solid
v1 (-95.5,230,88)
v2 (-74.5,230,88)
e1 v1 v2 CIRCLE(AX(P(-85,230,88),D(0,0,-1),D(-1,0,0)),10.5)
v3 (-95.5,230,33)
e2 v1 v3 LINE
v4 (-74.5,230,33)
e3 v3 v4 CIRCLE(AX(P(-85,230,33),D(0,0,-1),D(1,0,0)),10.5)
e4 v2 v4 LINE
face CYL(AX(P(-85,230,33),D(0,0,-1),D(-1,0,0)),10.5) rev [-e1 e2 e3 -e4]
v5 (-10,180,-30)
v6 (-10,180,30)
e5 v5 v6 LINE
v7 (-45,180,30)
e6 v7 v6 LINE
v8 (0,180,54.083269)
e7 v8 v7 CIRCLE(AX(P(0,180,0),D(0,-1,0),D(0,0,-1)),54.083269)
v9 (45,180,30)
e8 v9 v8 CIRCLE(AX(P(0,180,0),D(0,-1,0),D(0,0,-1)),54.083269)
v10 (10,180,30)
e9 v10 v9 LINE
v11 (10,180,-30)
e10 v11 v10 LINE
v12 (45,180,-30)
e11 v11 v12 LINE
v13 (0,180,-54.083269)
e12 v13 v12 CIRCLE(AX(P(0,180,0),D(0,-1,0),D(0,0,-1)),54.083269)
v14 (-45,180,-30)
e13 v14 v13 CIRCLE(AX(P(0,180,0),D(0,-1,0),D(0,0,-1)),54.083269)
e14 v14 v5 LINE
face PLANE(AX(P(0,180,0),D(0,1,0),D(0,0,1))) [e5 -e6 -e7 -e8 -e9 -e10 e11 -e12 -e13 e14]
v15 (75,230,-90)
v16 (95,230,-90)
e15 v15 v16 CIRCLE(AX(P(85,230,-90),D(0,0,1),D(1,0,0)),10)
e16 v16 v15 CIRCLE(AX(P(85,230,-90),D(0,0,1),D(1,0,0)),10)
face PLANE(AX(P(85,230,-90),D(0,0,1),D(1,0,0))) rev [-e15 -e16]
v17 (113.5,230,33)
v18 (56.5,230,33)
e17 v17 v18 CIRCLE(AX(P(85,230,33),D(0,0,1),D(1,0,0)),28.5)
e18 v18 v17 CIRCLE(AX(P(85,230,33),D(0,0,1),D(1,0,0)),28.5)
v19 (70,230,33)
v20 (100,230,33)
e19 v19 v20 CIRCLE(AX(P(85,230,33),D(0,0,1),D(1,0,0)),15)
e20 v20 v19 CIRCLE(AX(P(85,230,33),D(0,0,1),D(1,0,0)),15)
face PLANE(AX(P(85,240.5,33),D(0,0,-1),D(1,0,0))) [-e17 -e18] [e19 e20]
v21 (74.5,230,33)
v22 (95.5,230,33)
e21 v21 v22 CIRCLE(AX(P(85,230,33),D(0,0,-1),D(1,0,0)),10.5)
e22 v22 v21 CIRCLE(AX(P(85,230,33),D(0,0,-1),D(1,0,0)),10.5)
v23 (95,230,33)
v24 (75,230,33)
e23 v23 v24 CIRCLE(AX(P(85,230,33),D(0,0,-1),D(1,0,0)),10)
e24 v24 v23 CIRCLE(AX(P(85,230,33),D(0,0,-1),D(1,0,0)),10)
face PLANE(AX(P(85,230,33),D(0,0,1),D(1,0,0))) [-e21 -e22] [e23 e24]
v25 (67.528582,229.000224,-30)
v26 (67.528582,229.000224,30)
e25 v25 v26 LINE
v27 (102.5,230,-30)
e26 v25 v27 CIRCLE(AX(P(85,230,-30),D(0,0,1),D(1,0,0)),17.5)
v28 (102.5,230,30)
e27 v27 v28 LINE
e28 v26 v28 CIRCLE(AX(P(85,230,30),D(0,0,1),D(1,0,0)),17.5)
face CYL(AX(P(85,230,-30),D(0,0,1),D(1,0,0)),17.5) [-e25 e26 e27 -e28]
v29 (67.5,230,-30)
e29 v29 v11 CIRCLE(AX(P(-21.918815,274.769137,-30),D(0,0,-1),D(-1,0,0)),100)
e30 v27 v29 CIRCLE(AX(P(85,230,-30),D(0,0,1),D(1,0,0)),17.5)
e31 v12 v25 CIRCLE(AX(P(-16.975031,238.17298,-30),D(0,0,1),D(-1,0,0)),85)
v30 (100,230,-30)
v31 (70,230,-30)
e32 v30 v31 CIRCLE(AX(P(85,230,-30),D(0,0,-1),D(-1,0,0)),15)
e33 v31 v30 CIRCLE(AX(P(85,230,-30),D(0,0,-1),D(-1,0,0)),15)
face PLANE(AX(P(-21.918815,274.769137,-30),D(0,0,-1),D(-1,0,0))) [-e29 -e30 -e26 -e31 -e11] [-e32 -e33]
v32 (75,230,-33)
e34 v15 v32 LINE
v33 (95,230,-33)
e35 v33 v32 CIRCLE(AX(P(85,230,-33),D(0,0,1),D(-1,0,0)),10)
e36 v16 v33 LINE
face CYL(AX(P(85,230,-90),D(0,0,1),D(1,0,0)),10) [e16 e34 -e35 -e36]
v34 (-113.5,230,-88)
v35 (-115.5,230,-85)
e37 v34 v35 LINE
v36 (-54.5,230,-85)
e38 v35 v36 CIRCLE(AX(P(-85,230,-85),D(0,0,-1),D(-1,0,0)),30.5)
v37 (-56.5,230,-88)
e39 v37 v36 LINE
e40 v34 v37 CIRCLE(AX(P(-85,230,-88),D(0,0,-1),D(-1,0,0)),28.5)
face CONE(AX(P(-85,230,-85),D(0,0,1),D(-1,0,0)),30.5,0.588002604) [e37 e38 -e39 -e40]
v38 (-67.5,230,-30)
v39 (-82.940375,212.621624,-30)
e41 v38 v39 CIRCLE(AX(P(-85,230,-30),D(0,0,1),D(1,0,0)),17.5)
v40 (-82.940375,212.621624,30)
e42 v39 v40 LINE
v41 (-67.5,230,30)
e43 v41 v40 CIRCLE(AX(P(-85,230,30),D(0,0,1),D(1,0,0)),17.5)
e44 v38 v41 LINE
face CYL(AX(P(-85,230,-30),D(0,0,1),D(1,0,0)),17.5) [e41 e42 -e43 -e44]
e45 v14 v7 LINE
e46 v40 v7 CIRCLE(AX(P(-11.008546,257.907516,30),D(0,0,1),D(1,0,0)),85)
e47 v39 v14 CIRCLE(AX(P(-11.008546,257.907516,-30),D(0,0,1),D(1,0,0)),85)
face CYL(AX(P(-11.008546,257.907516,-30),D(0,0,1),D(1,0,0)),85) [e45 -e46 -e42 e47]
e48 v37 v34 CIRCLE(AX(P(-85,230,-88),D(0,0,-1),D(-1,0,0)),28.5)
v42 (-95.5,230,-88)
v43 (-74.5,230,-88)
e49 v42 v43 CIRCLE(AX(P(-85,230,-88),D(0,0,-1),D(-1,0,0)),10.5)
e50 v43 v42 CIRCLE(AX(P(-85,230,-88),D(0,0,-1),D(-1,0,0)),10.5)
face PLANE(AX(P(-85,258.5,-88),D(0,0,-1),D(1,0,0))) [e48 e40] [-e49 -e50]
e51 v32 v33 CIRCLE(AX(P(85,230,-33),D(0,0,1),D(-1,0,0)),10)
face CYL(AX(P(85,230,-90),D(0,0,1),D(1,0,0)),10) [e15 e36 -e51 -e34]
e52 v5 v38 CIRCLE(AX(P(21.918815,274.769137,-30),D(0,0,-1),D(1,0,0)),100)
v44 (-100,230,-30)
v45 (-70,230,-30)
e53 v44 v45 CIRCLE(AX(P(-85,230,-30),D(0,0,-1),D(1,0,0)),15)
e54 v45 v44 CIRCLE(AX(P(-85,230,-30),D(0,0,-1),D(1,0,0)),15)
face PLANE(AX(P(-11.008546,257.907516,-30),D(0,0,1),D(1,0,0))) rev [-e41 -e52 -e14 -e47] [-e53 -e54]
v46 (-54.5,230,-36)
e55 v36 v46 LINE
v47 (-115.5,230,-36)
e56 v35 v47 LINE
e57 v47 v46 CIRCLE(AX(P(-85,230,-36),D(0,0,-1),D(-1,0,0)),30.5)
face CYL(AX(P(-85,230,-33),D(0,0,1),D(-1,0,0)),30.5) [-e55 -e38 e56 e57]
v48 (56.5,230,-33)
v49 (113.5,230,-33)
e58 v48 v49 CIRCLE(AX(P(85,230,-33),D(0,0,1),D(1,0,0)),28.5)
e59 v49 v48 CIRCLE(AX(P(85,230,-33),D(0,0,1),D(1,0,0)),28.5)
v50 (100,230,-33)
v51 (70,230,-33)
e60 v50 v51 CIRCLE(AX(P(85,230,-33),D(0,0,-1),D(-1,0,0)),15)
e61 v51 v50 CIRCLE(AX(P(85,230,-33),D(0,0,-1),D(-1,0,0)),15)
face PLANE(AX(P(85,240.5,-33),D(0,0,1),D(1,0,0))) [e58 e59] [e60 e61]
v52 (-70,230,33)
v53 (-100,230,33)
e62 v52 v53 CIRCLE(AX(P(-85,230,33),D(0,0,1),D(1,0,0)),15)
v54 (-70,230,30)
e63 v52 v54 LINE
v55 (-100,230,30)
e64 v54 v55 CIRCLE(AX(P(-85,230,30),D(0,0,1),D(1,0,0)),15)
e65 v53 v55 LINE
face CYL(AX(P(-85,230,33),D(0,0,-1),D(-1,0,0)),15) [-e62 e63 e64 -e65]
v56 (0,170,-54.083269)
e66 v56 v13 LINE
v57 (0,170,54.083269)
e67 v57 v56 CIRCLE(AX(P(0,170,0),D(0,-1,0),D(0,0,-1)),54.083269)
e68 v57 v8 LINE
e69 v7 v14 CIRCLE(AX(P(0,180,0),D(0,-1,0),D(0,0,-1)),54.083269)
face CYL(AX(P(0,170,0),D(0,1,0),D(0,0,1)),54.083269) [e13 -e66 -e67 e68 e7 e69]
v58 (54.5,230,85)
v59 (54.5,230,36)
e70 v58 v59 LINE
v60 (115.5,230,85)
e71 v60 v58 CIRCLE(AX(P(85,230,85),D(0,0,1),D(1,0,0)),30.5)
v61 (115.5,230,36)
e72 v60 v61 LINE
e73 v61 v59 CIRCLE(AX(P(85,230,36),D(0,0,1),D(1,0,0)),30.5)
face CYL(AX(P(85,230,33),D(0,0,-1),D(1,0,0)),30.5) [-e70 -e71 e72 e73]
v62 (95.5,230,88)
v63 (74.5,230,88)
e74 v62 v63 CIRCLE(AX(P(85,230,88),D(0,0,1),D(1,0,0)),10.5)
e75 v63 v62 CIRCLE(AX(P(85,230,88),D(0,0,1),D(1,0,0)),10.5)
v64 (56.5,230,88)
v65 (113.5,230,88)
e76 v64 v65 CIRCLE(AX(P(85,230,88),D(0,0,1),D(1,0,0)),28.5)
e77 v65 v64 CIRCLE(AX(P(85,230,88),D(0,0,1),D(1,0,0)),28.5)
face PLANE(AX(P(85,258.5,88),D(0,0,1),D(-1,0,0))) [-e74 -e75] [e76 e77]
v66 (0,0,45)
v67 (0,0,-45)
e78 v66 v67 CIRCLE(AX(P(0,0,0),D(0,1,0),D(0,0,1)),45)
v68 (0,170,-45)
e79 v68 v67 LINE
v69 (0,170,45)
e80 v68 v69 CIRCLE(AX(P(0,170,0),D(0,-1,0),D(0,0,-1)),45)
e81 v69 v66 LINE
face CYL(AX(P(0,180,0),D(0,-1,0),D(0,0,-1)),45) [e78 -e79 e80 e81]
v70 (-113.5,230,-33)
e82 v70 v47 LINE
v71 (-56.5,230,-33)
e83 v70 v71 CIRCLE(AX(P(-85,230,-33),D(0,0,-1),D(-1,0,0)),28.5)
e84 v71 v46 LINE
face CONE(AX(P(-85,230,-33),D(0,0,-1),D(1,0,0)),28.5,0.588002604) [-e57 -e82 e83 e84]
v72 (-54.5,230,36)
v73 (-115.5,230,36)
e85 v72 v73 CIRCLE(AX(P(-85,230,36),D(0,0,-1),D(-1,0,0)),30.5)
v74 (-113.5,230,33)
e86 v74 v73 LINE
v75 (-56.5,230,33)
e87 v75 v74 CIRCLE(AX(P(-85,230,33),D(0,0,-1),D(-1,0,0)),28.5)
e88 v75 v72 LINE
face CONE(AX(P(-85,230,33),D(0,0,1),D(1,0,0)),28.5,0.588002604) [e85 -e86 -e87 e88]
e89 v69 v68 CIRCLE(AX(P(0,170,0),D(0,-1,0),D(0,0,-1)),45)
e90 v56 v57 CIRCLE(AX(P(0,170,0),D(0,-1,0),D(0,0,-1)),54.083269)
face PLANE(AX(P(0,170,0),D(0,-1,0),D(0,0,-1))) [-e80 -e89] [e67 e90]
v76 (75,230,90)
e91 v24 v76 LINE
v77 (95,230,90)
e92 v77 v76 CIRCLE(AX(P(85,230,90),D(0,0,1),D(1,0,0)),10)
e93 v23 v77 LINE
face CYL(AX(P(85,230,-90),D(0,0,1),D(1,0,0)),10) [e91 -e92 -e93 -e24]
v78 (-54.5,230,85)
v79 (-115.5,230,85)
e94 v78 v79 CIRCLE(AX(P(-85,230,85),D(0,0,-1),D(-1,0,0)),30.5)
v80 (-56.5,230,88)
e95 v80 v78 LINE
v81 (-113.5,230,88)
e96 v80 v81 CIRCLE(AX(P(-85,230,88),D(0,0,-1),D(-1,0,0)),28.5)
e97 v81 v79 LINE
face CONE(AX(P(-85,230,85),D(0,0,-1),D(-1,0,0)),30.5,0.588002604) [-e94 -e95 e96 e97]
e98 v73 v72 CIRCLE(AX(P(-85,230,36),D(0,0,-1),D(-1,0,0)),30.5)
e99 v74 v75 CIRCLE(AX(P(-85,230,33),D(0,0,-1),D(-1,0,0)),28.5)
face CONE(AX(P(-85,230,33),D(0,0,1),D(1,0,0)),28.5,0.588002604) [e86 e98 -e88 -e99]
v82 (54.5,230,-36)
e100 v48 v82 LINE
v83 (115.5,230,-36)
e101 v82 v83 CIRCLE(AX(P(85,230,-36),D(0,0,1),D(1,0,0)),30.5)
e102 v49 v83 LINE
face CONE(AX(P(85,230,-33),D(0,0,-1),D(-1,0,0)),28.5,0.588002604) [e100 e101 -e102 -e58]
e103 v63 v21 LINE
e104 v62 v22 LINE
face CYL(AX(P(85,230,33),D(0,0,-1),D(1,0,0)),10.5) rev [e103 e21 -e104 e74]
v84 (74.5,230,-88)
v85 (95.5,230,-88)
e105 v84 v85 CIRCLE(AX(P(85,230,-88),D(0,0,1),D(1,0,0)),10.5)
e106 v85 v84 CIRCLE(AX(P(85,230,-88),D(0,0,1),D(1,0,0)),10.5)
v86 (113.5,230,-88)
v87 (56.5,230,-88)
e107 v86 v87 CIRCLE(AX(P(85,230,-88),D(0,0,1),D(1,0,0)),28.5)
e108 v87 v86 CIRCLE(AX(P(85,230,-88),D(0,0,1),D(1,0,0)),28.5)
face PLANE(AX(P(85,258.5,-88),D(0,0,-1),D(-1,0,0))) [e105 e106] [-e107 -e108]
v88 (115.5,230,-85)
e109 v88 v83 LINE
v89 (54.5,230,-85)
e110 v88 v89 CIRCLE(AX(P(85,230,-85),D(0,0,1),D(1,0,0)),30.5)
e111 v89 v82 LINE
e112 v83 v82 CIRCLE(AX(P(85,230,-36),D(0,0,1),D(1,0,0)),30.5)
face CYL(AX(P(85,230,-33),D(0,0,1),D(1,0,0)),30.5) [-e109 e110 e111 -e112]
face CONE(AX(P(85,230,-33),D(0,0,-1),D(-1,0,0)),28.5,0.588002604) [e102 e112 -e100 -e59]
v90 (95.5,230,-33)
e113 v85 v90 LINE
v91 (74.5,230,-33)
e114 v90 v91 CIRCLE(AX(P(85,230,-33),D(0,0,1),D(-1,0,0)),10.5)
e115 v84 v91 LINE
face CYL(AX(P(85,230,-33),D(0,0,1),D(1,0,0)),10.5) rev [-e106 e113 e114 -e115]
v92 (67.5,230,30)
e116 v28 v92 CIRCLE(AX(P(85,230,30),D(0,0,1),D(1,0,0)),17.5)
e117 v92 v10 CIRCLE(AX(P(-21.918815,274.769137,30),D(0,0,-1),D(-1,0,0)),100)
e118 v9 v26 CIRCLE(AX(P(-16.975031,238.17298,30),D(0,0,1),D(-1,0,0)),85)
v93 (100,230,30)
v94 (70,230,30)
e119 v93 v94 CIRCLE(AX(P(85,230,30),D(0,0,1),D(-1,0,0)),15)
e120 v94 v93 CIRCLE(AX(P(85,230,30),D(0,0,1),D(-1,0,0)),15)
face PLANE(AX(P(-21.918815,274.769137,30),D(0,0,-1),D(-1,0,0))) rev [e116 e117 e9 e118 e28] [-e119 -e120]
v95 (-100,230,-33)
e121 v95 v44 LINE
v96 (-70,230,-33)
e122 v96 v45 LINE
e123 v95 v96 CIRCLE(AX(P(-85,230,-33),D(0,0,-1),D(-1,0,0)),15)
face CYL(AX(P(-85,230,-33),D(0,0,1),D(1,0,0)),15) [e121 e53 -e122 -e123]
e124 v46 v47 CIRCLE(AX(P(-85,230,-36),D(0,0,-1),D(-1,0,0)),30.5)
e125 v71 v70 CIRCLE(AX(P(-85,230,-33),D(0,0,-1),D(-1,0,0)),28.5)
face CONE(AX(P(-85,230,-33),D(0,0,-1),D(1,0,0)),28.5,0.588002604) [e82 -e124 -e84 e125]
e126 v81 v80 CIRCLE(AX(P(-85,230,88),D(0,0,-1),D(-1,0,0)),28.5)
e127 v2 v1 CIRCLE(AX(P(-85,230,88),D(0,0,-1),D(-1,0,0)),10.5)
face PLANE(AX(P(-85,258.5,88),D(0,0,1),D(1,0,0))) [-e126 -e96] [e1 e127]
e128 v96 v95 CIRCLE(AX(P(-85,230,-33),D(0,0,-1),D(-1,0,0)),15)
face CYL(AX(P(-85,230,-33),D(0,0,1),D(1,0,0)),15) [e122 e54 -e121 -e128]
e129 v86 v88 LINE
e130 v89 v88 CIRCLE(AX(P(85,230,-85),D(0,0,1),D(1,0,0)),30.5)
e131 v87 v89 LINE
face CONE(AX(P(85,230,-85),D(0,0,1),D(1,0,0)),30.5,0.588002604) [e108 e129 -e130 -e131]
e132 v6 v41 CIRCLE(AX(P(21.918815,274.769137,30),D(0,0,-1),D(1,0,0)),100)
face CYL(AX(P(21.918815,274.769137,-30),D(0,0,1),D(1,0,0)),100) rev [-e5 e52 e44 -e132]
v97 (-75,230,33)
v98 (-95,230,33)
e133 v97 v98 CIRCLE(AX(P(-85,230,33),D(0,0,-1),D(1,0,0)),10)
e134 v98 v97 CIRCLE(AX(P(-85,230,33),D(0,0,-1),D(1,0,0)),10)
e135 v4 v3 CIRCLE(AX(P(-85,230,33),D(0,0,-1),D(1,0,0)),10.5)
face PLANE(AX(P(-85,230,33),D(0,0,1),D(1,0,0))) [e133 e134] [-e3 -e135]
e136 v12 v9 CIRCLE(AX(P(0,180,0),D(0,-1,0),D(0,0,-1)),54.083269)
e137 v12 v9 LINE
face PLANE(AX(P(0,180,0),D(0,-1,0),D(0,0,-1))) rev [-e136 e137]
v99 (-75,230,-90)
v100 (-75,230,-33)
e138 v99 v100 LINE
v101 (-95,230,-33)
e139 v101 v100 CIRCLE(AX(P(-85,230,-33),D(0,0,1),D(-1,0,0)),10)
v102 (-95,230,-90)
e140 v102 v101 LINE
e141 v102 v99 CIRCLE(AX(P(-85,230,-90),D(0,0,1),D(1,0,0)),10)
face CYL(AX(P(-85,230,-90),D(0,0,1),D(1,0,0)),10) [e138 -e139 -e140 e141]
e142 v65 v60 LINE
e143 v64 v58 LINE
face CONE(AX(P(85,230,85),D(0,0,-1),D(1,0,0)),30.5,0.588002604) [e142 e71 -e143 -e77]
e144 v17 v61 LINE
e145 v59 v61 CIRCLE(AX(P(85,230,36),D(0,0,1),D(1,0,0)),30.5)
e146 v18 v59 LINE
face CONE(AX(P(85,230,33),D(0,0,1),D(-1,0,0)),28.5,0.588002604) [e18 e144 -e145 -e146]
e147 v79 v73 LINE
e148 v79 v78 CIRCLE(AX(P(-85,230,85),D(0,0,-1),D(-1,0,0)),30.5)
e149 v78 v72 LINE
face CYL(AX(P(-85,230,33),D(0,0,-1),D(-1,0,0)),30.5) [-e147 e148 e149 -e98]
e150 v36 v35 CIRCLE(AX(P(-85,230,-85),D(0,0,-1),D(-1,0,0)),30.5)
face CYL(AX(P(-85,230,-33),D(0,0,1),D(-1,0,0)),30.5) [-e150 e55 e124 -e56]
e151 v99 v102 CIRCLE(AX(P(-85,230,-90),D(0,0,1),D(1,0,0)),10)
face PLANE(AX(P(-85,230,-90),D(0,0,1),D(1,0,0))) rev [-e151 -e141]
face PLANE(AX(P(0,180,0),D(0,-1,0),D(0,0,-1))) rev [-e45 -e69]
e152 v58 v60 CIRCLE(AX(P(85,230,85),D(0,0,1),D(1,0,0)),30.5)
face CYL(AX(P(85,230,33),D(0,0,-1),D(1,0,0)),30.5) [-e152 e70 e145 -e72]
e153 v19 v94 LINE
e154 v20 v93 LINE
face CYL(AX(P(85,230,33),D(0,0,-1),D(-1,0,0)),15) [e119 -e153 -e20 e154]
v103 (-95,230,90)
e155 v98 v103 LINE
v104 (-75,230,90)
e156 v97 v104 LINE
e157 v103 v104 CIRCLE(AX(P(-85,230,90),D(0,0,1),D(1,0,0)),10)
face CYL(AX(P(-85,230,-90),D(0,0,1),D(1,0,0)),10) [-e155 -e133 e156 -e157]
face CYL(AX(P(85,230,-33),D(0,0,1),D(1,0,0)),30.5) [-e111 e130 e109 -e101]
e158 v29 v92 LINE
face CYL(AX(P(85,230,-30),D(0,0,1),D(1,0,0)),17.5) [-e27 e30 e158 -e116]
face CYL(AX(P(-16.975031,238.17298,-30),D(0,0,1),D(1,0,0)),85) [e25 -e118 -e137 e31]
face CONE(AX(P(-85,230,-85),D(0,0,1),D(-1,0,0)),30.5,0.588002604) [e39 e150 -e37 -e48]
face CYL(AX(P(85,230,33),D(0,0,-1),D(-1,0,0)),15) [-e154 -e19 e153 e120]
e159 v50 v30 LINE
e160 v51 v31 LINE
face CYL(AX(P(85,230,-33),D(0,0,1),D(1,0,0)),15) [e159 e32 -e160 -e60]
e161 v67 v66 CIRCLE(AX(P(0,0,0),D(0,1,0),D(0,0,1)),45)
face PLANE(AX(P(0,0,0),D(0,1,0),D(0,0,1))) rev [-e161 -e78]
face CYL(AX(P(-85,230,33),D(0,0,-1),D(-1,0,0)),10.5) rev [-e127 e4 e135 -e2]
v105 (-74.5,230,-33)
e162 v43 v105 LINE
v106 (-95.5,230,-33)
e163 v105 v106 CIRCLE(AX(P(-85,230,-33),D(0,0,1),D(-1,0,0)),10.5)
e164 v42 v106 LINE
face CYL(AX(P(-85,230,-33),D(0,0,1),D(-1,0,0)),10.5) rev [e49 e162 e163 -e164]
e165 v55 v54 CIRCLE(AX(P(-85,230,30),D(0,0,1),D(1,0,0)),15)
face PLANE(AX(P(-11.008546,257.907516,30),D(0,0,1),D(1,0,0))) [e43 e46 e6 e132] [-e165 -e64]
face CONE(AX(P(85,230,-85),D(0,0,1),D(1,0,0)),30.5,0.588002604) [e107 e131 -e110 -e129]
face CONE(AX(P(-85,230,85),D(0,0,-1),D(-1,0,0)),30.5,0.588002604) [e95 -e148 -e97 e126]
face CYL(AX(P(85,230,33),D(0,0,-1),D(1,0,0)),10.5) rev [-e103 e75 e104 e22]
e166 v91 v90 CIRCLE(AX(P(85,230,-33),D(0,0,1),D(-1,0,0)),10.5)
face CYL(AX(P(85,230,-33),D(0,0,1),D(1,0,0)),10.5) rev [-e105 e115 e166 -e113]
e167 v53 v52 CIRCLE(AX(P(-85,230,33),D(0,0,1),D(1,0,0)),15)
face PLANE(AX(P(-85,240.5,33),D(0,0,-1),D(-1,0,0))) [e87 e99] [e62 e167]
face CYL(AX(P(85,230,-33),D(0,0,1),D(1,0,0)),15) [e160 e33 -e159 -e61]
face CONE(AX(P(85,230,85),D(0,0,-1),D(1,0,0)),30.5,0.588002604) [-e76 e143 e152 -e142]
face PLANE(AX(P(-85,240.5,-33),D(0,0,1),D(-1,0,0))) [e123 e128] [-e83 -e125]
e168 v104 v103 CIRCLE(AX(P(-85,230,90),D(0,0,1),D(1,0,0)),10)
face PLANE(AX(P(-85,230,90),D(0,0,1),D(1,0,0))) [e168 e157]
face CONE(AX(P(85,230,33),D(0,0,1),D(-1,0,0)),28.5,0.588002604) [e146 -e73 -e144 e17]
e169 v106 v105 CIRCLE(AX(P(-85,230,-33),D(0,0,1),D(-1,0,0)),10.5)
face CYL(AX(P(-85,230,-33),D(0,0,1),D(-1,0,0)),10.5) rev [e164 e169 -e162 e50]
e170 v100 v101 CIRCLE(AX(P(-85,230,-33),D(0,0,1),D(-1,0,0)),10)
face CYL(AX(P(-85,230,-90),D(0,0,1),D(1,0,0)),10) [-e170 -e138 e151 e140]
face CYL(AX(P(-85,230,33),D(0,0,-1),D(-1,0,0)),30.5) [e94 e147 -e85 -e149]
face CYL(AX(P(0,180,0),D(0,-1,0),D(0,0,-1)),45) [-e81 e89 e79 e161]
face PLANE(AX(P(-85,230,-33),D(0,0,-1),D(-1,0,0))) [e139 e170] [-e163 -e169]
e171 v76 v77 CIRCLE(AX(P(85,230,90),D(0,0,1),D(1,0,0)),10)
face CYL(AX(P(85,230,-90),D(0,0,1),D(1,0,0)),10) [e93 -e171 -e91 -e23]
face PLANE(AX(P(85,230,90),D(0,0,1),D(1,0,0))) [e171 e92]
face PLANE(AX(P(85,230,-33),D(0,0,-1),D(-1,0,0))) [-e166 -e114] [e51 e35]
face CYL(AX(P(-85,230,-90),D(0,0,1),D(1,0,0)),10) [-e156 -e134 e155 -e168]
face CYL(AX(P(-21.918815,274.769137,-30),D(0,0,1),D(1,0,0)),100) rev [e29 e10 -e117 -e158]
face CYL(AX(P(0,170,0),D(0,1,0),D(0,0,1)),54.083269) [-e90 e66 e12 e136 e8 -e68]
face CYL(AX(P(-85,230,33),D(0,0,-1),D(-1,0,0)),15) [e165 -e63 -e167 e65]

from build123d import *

# Parameters (mm, degrees)
SKETCH1_R                  = 45
BOSS_EXTRUDE1_DEPTH        = 180
BOSS_EXTRUDE2_DEPTH        = 90
BOSS_EXTRUDE2_DEPTH_BACK   = 90
SKETCH3_R                  = 10
BOSS_EXTRUDE2_2_DEPTH      = 90
BOSS_EXTRUDE2_2_DEPTH_BACK = 90
BOSS_EXTRUDE3_DEPTH        = 30
BOSS_EXTRUDE3_DEPTH_BACK   = 30
SKETCH5_R                  = 54.083269132
BOSS_EXTRUDE4_DEPTH        = 10
SKETCH6_R                  = 15
BOSS_EXTRUDE5_DEPTH        = 3
BOSS_EXTRUDE6_START        = 3
SKETCH7_R                  = 15
BOSS_EXTRUDE6_DEPTH        = 3


with BuildPart() as part:
    # Sketch1 → Boss-Extrude1 (new body)
    with BuildSketch(Plane(origin=(0, 0, 0), x_dir=(1, 0, 0), z_dir=(0, 1, 0))):
        with Locations(Location((0, 0, 0), (0, 0, 90))):
            Circle(SKETCH1_R)
    extrude(amount=BOSS_EXTRUDE1_DEPTH)



with BuildPart() as body_2:
    # Sketch3 → Boss-Extrude2 (new, two sides: drawn at the far end of the back side and taken through both)
    with BuildSketch(Plane.XY.offset(-BOSS_EXTRUDE2_DEPTH_BACK)):
        with Locations((85, 230)):
            Circle(SKETCH3_R)
    extrude(amount=BOSS_EXTRUDE2_DEPTH + BOSS_EXTRUDE2_DEPTH_BACK)


with BuildPart() as body_3:
    # Sketch3 → Boss-Extrude2 2 (new, two sides: drawn at the far end of the back side and taken through both)
    with BuildSketch(Plane.XY.offset(-BOSS_EXTRUDE2_2_DEPTH_BACK)):
        with Locations((-85, 230)):
            Circle(SKETCH3_R)
    extrude(amount=BOSS_EXTRUDE2_2_DEPTH + BOSS_EXTRUDE2_2_DEPTH_BACK)


with BuildPart() as part_1:
    add(part.part)

    add(body_2.part)  # Boss-Extrude3 merges body 2

    add(body_3.part)  # Boss-Extrude3 merges body 3
    # Sketch4 → Boss-Extrude3 (add, two sides: drawn at the far end of the back side and taken through both)
    with BuildSketch(Plane.XY.offset(-BOSS_EXTRUDE3_DEPTH_BACK)):
        with BuildLine():
            Line((-45, 180), (-10, 180))
            ThreePointArc((-10, 180), (-43.69905694, 199.308584519), (-67.5, 230))
            ThreePointArc((-67.5, 230), (-98.082305532, 241.623393737), (-82.940375083, 212.621624207))
            ThreePointArc((-82.940375083, 212.621624207), (-66.424952125, 193.455813577), (-45, 180))
        make_face()
        with BuildLine():
            Line((10, 180), (45, 180))
            ThreePointArc((45, 180), (60.253550288, 202.66599047), (67.528581994, 229.00022359))
            ThreePointArc((67.528581994, 229.00022359), (102.492853042, 230.500092441), (67.5, 230))
            ThreePointArc((67.5, 230), (43.69905694, 199.308584519), (10, 180))
        make_face()
    extrude(amount=BOSS_EXTRUDE3_DEPTH + BOSS_EXTRUDE3_DEPTH_BACK)

    # Sketch5 → Boss-Extrude4 (add)
    with BuildSketch(Plane.XZ.offset(-180)):
        with Locations(Location((0, 0, 0), (0, 0, 33.690067526))):
            Circle(SKETCH5_R)
    extrude(amount=BOSS_EXTRUDE4_DEPTH)

    # Sketch6 → Boss-Extrude5 (add)
    with BuildSketch(Plane.XY.offset(30)):
        with Locations((-85, 230)):
            Circle(SKETCH6_R)
        with Locations(Location((85, 230, 0), (0, 0, 180))):
            Circle(SKETCH6_R)
    extrude(amount=BOSS_EXTRUDE5_DEPTH)

    # Sketch7 → Boss-Extrude6 (add)
    with BuildSketch(Plane(origin=(0, 0, -30), x_dir=(-1, 0, 0), z_dir=(0, 0, -1)).offset(BOSS_EXTRUDE6_START)):
        with Locations((-85, 230)):
            Circle(SKETCH7_R)
        with Locations(Location((85, 230, 0), (0, 0, 180))):
            Circle(SKETCH7_R)
    extrude(amount=-BOSS_EXTRUDE6_DEPTH)

    # Sketch8 → Revolve1 (revolve)
    with BuildSketch(Plane(origin=(-85, 0, 0), x_dir=(0, 0, -1), z_dir=(1, 0, 0)), mode=Mode.PRIVATE) as revolve1_sk:
        Polygon((-33, 240.5), (-33, 258.5), (-36, 260.5), (-85, 260.5), (-88, 258.5), (-88, 240.5), align=None)
    revolve1 = revolve(revolve1_sk.sketch.rotate(Axis((-85, 230, 33), (0, 0, 1)), 90), axis=Axis((-85, 230, 33), (0, 0, 1)))

    # Mirror1: Revolve1 across plane
    add(revolve1.mirror(Plane(origin=(0, 0, 0), x_dir=(0, 0, 1), z_dir=(1, 0, 0))))

    # Mirror2: Revolve1 across plane
    add(revolve1.mirror(Plane.XY))

    # Mirror2 copy 1 sketch → Mirror2 copy 1 (revolve)
    with BuildSketch(Plane.ZY.offset(-85)):
        Polygon((-33, 240.5), (-33, 258.5), (-36, 260.5), (-85, 260.5), (-88, 258.5), (-88, 240.5), align=None)
    revolve(axis=Axis((85, 230, -33), (0, 0, -1)))


solid = part_1.part
